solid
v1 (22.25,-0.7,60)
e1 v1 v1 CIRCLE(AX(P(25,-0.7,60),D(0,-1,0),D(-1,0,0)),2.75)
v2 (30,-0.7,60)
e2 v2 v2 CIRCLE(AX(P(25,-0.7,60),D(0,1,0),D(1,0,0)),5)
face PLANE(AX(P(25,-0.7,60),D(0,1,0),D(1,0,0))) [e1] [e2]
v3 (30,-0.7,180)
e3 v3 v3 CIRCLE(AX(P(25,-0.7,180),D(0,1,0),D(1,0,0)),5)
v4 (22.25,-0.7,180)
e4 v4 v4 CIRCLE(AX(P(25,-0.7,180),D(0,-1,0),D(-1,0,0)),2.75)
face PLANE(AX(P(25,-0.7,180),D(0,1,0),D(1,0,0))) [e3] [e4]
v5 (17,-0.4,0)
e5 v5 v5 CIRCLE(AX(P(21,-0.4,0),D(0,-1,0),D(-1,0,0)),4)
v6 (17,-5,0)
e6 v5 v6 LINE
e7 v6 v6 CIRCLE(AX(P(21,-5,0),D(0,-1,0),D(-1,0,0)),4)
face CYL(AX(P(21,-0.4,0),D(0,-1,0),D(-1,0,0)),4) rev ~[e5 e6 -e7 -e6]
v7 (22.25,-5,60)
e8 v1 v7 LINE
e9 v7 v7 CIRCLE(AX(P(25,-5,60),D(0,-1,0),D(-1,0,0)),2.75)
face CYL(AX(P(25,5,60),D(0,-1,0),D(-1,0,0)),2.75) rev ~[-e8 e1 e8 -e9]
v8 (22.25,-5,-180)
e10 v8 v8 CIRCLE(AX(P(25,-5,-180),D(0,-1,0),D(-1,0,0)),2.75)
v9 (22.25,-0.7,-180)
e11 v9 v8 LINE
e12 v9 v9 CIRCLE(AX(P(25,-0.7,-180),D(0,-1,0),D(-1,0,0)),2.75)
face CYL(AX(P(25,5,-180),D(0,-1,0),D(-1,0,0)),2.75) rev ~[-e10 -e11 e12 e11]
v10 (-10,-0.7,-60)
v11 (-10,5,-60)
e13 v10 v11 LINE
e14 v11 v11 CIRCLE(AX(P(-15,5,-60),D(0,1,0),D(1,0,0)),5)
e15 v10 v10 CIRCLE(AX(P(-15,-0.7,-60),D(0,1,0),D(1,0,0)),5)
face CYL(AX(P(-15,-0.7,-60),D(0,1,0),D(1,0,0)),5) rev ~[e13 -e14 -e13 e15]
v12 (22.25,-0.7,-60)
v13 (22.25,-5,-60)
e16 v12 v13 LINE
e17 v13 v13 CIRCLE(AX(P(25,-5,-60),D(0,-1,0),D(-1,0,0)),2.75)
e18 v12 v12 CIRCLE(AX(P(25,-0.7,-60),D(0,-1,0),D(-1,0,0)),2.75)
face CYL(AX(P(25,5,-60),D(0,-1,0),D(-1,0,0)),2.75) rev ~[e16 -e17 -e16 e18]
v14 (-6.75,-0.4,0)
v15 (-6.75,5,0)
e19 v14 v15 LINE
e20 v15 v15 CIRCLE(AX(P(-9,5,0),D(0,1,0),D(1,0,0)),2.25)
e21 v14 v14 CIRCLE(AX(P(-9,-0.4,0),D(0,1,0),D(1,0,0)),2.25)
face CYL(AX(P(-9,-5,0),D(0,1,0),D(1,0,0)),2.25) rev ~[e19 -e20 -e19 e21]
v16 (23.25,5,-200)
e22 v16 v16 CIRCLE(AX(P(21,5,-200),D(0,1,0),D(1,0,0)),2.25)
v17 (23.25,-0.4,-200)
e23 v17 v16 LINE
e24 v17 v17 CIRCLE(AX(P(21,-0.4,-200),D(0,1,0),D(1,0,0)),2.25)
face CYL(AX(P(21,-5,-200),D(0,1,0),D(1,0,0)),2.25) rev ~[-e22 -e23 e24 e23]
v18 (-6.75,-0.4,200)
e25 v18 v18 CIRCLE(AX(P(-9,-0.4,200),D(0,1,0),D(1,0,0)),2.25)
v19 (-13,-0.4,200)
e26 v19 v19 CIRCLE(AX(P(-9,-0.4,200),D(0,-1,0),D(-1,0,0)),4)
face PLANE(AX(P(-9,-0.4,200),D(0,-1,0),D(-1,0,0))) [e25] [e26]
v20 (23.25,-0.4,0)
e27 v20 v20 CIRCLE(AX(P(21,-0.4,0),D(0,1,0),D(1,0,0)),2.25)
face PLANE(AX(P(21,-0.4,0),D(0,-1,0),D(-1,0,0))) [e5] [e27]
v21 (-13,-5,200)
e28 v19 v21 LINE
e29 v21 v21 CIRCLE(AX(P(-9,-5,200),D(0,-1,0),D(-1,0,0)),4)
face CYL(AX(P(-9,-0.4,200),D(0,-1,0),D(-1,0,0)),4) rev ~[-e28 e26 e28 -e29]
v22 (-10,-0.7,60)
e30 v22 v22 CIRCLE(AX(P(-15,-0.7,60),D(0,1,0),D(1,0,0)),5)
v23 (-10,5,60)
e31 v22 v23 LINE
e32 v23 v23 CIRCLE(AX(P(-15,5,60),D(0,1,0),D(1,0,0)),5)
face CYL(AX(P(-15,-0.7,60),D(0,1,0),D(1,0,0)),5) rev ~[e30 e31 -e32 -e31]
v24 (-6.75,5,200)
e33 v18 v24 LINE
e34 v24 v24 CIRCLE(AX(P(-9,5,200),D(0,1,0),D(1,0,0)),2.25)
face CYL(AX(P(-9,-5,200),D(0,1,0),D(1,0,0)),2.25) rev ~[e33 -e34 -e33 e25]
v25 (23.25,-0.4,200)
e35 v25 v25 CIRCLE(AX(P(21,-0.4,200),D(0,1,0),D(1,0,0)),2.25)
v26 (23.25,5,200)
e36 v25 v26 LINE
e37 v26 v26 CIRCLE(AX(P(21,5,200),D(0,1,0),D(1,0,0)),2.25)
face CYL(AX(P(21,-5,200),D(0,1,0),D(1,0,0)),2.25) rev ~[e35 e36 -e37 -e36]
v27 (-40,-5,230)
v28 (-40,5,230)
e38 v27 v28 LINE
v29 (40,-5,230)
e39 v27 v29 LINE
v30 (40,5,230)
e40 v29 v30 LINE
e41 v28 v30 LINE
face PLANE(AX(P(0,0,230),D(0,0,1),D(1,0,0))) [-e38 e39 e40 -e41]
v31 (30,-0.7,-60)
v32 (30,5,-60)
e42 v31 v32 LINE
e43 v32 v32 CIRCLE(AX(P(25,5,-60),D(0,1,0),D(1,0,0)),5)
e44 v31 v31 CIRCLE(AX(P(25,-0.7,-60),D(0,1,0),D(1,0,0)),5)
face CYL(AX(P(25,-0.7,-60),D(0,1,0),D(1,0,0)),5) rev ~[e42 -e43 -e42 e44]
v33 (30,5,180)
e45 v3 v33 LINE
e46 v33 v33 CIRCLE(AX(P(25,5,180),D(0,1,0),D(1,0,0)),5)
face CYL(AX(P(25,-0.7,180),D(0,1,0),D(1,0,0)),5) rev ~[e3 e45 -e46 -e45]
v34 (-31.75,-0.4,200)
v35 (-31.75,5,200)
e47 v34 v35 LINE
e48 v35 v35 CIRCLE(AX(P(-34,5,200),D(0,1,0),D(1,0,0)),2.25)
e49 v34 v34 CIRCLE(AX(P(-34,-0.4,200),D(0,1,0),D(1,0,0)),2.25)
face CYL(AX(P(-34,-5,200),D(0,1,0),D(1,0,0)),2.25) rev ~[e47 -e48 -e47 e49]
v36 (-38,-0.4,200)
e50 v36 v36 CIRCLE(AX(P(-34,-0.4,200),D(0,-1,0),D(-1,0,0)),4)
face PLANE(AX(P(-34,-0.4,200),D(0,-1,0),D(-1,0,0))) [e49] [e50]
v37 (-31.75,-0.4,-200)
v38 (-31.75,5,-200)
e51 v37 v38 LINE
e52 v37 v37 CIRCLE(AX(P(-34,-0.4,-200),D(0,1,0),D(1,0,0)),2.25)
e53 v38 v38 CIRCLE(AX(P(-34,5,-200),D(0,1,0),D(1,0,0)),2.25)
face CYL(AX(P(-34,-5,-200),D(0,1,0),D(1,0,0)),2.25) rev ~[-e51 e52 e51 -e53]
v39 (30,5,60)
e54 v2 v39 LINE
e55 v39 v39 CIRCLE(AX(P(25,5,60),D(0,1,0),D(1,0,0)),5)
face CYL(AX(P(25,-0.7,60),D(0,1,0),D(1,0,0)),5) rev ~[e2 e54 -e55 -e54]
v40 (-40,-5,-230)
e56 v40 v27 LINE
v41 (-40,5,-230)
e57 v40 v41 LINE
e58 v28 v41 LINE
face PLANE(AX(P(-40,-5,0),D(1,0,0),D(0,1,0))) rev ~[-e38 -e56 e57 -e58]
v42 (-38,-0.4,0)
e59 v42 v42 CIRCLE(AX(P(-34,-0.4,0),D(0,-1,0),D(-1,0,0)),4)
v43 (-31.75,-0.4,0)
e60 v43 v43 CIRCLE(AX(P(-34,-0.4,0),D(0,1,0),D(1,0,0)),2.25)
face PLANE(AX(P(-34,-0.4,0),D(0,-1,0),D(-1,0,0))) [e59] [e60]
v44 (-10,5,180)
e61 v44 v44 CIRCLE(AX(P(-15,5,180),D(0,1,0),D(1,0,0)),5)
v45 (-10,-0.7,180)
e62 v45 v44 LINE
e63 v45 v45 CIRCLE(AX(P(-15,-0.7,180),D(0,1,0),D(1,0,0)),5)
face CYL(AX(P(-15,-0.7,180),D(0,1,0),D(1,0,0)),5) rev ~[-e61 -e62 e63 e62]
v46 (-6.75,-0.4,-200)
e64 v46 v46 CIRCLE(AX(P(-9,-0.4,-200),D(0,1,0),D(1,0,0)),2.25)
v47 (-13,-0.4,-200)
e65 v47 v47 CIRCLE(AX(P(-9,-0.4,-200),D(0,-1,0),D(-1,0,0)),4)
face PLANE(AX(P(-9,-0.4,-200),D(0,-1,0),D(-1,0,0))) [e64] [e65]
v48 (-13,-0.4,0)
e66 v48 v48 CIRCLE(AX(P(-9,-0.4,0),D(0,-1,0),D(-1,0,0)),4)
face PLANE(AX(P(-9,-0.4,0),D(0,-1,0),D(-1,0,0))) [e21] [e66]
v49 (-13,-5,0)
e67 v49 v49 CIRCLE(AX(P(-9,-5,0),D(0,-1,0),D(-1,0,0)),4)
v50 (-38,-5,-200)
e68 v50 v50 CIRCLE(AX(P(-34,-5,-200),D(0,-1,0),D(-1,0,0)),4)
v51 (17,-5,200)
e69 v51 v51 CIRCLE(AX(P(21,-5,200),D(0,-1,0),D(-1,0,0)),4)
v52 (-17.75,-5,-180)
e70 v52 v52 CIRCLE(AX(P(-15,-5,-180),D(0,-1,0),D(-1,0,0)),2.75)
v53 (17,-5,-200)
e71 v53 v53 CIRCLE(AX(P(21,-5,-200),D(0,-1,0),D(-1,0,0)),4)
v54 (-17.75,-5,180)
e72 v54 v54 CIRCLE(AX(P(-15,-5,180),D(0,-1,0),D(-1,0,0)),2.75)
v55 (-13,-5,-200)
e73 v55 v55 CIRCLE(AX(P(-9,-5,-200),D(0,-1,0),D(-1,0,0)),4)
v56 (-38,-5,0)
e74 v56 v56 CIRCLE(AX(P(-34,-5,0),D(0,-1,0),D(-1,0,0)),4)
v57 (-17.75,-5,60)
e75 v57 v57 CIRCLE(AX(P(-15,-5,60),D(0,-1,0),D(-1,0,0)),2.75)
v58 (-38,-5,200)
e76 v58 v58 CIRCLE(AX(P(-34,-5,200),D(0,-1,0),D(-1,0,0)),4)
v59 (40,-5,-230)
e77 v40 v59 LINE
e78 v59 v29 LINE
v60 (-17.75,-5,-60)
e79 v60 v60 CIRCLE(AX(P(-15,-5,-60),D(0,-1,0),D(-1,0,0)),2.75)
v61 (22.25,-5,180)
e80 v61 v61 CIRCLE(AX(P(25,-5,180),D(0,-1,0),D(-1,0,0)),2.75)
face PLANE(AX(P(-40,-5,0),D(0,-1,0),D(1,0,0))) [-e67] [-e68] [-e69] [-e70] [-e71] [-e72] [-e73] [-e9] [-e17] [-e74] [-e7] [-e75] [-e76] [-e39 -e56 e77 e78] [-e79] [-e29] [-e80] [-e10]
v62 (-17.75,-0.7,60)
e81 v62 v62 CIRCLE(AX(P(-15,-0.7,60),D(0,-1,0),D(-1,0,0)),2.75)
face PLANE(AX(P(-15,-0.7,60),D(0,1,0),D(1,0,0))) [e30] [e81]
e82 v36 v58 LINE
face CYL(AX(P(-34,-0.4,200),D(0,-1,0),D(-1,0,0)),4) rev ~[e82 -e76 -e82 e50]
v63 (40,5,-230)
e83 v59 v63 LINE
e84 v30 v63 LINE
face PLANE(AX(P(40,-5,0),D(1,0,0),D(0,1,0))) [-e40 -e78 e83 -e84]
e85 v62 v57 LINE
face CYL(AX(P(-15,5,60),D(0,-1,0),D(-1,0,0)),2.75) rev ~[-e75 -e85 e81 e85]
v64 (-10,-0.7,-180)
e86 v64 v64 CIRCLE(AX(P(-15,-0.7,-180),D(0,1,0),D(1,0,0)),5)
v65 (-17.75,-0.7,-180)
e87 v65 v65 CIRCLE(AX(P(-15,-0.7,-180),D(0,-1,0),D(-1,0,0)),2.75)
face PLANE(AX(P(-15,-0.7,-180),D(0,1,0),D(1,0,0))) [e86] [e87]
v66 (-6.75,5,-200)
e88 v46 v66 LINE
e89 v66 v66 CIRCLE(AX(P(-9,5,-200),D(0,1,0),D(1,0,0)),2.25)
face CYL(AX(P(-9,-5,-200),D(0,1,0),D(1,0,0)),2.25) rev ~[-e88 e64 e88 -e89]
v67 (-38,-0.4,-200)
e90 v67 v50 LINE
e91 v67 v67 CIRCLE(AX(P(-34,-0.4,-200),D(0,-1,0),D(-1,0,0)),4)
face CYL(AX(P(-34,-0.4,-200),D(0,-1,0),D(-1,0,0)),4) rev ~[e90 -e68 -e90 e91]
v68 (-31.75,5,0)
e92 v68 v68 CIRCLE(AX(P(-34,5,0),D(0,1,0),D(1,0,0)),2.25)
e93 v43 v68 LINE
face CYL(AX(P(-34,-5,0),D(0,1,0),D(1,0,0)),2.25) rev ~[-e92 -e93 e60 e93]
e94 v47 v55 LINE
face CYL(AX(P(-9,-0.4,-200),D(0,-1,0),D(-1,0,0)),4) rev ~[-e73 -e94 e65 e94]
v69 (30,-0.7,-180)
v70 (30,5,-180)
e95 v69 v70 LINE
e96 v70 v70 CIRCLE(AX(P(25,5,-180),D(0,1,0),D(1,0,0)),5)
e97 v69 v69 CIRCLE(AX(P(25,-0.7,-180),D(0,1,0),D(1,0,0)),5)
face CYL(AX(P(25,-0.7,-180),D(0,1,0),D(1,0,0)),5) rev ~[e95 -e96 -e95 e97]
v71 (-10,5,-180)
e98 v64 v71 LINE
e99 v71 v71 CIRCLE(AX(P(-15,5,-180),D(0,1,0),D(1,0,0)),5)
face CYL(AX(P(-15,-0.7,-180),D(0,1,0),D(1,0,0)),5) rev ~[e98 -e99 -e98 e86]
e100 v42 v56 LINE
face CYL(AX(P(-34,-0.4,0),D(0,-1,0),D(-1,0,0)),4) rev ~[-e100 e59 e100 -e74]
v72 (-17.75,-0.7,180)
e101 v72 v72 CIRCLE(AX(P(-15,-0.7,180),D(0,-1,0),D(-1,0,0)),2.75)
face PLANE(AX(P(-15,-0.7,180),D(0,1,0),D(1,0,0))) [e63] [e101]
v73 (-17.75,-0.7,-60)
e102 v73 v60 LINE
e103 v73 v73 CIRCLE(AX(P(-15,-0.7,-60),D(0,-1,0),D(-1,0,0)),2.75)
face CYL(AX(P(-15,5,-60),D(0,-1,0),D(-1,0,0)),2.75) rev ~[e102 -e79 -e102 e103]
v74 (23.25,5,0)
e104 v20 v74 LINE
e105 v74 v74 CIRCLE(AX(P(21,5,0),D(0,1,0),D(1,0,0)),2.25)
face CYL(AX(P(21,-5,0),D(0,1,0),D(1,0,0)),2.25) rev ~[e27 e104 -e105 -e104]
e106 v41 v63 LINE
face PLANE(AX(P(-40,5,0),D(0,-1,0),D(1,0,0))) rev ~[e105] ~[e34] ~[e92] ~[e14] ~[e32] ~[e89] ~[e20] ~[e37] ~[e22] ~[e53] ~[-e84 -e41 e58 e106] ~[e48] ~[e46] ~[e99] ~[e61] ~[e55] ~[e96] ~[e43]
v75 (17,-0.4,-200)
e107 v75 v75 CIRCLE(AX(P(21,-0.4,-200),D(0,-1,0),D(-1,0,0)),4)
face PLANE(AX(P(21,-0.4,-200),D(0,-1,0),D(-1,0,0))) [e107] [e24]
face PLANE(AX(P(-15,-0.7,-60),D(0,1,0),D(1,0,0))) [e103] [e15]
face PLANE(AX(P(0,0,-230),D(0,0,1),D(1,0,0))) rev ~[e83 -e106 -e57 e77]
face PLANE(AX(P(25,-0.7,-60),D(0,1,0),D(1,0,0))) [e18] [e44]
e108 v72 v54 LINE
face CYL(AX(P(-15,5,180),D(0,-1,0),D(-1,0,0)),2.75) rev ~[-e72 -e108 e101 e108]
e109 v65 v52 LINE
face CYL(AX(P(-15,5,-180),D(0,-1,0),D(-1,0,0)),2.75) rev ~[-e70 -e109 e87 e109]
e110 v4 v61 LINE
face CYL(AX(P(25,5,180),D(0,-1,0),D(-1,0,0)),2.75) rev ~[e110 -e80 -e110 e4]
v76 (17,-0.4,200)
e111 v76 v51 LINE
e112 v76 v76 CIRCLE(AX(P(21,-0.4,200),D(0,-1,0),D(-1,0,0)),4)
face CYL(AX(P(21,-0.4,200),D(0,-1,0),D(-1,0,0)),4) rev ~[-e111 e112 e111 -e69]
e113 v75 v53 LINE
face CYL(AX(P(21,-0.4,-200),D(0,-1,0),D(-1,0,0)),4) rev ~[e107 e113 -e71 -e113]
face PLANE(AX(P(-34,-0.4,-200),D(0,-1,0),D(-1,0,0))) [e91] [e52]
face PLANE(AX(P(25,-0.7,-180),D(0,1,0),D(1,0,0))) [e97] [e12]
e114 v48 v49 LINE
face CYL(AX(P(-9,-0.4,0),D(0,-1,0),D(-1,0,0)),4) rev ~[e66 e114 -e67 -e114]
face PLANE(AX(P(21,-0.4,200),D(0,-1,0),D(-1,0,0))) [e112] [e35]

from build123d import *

# Parameters (mm, degrees)
SKETCH_1_W                = 80
SKETCH_1_H                = 10
EXTRUDE_1_DEPTH           = 230
HOLE_WIZARD_1_D           = 4.5
HOLE_WIZARD_1_CBORE_D     = 8
HOLE_WIZARD_1_CBORE_DEPTH = 4.6
HOLE_WIZARD_2_D           = 5.5
HOLE_WIZARD_2_CBORE_D     = 10
HOLE_WIZARD_2_CBORE_DEPTH = 5.7


with BuildPart() as part:
    # 草图1 → 凸台-拉伸1 (new, symmetric)
    with BuildSketch(Plane.XY):
        Rectangle(SKETCH_1_W, SKETCH_1_H)
    extrude(amount=EXTRUDE_1_DEPTH, both=True)

    # 打孔尺寸(%根据)内六角圆柱头螺钉的类型1 (through all)
    with Locations(Plane(origin=(0, -5, 0), x_dir=(-1, 0, 0), z_dir=(0, -1, 0))):
        with Locations((34, -200), (9, -200), (-21, -200), (34, 0), (9, 0), (-21, 0), (34, 200), (9, 200), (-21, 200)):
            CounterBoreHole(HOLE_WIZARD_1_D / 2, HOLE_WIZARD_1_CBORE_D / 2, HOLE_WIZARD_1_CBORE_DEPTH)

    # 打孔尺寸(%根据)内六角圆柱头螺钉的类型2 (through all)
    with Locations(Plane(origin=(0, 5, 0), x_dir=(1, 0, 0), z_dir=(0, 1, 0))):
        with Locations((-15, -180), (25, -180), (-15, -60), (25, -60), (25, 60), (25, 180), (-15, 180), (-15, 60)):
            CounterBoreHole(HOLE_WIZARD_2_D / 2, HOLE_WIZARD_2_CBORE_D / 2, HOLE_WIZARD_2_CBORE_DEPTH)


solid = part.part
